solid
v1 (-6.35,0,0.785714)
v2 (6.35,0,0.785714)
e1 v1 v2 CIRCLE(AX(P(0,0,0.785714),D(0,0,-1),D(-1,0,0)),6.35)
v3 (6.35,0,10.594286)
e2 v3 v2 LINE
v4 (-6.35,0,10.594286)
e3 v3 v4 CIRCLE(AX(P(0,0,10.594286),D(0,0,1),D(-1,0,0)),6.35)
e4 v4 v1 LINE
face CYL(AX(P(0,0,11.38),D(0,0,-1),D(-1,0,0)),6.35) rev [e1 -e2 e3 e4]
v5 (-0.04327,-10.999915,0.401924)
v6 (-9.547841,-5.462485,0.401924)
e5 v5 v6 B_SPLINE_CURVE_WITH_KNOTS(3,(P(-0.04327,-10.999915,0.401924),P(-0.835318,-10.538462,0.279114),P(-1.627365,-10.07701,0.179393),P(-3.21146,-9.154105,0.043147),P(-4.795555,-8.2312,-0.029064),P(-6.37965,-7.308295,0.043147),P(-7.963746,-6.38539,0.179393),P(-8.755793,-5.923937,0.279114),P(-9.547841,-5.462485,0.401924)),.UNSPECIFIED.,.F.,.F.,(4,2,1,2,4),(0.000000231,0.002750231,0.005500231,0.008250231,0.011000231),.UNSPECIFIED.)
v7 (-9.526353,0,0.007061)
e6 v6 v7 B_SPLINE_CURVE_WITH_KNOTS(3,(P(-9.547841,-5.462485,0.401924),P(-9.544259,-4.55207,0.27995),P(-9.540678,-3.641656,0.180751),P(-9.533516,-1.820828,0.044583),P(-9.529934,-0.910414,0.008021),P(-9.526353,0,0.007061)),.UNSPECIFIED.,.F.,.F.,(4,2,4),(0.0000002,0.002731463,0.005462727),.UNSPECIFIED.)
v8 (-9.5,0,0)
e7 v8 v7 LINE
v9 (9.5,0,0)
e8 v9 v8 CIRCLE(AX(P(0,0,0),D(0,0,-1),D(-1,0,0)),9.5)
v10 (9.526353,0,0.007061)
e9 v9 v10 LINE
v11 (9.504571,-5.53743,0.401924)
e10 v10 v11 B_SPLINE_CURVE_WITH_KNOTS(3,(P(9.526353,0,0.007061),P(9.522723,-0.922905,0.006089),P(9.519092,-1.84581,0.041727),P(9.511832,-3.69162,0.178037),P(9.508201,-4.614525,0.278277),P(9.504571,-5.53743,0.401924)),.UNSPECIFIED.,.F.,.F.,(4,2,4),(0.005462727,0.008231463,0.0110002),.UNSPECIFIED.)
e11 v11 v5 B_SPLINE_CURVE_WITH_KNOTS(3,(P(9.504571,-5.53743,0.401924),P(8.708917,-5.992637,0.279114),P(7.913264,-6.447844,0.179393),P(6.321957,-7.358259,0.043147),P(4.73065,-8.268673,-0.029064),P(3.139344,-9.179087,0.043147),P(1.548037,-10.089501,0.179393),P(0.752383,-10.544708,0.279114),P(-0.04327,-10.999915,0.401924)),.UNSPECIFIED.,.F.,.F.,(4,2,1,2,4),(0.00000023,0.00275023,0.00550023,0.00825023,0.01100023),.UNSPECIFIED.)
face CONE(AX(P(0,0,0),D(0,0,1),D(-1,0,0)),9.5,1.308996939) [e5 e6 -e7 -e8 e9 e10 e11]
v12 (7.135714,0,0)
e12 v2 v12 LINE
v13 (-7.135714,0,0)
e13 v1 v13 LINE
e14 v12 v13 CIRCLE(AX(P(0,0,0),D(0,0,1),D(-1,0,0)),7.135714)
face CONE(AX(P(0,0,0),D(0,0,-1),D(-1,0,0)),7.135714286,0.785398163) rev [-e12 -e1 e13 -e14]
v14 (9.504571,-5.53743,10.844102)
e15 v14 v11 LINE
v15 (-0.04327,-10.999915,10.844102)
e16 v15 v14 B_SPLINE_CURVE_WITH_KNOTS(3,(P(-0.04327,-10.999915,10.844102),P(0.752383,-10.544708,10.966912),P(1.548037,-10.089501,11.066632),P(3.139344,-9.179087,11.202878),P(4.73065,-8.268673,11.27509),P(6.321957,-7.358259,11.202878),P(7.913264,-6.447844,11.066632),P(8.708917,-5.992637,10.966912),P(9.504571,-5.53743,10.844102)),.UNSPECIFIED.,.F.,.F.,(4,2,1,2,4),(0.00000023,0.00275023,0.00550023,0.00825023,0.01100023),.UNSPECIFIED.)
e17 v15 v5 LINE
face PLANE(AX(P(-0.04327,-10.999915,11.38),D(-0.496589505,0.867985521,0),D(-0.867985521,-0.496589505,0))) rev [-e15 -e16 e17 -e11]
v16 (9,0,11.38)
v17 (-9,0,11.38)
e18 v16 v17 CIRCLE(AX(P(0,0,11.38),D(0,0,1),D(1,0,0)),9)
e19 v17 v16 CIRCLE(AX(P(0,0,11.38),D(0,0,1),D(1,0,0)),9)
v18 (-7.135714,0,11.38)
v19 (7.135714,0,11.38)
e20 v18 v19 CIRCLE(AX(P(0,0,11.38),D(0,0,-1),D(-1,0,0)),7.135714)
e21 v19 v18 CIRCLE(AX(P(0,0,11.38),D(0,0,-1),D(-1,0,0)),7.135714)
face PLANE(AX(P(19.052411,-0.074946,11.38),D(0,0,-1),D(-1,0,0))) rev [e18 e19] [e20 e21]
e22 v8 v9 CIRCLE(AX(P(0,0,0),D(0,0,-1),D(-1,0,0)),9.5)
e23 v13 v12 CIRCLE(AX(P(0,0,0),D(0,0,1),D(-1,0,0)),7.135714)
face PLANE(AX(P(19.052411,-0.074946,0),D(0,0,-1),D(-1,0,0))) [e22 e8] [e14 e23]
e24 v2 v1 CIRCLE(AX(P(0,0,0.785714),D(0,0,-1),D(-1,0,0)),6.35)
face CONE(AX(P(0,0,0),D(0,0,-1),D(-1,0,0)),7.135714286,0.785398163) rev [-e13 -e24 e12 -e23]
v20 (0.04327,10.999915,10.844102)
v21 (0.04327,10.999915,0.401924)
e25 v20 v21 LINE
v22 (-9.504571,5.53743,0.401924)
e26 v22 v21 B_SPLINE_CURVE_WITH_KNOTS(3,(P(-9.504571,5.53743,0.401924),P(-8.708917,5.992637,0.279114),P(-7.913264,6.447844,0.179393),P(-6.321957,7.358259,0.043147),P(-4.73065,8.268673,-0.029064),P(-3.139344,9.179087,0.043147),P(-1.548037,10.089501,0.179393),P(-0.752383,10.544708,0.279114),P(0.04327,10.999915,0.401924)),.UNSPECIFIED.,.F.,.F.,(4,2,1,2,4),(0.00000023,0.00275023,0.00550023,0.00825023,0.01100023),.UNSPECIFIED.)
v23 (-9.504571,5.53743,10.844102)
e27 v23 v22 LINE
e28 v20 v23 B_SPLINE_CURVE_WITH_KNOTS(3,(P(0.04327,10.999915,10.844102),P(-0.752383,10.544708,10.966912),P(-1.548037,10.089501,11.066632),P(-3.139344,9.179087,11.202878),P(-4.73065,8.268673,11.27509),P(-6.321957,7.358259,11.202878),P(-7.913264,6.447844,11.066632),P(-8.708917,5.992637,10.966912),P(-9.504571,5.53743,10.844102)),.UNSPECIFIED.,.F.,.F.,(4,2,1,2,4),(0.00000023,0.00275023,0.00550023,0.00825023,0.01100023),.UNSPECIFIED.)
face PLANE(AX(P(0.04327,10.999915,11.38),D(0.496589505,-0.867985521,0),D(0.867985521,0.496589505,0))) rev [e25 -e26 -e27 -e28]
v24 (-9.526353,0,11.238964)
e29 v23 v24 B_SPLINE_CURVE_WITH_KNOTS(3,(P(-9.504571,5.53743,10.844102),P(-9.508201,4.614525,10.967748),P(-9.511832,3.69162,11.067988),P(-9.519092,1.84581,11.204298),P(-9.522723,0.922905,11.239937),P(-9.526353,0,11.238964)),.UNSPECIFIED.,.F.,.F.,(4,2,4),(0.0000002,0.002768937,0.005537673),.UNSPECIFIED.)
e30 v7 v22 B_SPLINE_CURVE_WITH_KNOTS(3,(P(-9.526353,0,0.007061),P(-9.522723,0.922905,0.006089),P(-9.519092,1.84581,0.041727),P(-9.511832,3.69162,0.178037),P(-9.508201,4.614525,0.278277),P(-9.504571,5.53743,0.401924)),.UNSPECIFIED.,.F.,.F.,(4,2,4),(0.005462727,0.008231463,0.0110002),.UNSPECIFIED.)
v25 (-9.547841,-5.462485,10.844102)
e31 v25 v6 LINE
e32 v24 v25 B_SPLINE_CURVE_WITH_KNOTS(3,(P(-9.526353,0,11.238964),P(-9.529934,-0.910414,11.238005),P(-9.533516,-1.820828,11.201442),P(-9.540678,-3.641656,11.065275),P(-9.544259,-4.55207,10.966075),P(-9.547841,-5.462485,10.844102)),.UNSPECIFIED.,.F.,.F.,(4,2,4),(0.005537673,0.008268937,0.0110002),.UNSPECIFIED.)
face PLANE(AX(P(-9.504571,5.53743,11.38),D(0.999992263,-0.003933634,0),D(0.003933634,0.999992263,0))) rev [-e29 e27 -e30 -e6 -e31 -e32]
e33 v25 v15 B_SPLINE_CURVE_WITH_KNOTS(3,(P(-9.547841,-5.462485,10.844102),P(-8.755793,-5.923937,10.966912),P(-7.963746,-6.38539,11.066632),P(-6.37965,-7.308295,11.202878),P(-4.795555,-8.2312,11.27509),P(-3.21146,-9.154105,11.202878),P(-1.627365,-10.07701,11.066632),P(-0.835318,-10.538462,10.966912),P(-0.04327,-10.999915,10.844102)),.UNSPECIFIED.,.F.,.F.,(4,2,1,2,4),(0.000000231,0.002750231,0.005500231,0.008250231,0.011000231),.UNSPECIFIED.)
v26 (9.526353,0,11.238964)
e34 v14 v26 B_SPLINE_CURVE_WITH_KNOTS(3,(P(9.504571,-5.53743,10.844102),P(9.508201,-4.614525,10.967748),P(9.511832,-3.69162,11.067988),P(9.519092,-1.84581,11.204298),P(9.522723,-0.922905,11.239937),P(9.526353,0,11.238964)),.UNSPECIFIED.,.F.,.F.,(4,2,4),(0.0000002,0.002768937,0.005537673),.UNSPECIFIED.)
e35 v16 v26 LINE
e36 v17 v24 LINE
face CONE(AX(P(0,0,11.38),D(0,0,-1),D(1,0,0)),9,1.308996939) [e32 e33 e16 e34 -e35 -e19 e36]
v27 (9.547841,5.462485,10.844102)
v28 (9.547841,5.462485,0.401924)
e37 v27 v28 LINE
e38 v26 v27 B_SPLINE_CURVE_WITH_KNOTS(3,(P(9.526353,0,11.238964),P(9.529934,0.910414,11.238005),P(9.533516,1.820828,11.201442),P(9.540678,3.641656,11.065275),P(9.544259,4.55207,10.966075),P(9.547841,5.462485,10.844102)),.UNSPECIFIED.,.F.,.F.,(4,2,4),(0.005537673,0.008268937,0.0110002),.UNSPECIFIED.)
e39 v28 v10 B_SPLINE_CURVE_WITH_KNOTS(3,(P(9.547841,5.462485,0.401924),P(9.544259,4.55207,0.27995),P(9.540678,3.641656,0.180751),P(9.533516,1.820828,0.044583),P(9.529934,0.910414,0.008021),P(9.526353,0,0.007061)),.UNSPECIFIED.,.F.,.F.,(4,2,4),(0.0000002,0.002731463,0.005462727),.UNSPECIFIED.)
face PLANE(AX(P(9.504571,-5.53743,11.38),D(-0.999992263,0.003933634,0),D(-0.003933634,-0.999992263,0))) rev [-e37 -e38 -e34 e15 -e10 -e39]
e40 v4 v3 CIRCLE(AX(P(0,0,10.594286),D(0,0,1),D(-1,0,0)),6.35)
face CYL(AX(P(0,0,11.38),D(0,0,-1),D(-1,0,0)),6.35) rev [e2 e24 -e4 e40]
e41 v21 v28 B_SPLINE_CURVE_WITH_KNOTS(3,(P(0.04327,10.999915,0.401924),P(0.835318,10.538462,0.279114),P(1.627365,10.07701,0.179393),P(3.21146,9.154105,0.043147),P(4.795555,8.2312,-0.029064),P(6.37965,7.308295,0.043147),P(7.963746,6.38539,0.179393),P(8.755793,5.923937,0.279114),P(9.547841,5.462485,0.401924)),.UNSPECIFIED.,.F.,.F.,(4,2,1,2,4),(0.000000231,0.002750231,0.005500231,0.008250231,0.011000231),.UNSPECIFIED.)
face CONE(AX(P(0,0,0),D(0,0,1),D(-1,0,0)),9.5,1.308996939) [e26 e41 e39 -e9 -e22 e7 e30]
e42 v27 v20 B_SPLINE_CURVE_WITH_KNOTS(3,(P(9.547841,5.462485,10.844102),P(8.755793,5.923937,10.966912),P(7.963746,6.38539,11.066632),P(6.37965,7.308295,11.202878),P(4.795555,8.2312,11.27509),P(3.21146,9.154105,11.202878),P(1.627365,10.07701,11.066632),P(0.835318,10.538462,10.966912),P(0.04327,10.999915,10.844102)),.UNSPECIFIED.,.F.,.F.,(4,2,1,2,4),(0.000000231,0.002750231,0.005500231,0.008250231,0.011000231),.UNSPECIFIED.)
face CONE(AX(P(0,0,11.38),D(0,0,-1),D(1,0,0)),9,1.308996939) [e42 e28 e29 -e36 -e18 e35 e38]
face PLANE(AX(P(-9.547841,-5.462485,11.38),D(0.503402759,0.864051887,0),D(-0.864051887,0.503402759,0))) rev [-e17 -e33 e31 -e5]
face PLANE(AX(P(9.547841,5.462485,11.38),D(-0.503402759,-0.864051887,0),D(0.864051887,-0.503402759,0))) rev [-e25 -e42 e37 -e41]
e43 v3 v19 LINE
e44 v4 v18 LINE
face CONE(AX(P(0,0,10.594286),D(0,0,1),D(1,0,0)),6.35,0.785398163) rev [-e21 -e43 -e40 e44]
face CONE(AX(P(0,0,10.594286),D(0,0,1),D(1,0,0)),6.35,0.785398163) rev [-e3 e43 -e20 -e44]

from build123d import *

# Parameters (mm, degrees)
SKETCH1_R          = 6.35
BASE_EXTRUDE_DEPTH = 11.38
SKETCH2_OUTSIDE_W  = 172.782
SKETCH2_OUTSIDE_H  = 175.686
SKETCH2_OUTSIDE_R  = 9.5
CUT_EXTRUDE1_DEPTH = 19.484149703
CUT_EXTRUDE1_DRAFT = -75
SKETCH3_OUTSIDE_W  = 172.782
SKETCH3_OUTSIDE_H  = 175.686
SKETCH3_OUTSIDE_R  = 9
CUT_EXTRUDE2_DEPTH = 19.484149703
CUT_EXTRUDE2_DRAFT = -75
CHAMFER1_SIZE      = 0.785714286


with BuildPart() as part:
    # Sketch1 → Base-Extrude (new body)
    with BuildSketch(Plane.XY):
        Polygon((0.043269974, 10.999914896), (-9.504570752, 5.537430344), (-9.547840726, -5.462484551), (-0.043269974, -10.999914896), (9.504570752, -5.537430344), (9.547840726, 5.462484551), align=None)
        Circle(SKETCH1_R, mode=Mode.SUBTRACT)
    extrude(amount=BASE_EXTRUDE_DEPTH)


with BuildPart() as cut_extrude1_tool:
    # Sketch2 outside → Cut-Extrude1 (with draft: the straight prism first)
    with BuildSketch(Plane(origin=(0, 0, 0), x_dir=(-1, 0, 0), z_dir=(0, 0, -1))):
        Rectangle(SKETCH2_OUTSIDE_W, SKETCH2_OUTSIDE_H)
        Circle(SKETCH2_OUTSIDE_R, mode=Mode.SUBTRACT)
    extrude(amount=-CUT_EXTRUDE1_DEPTH)
    # Cut-Extrude1: the draft: its side faces are tilted about the plane it starts from
    cut_extrude1_sides = [cut_extrude1_tool.faces().sort_by_distance(p)[0] for p in [
        (0, -87.843, 9.742074851),
        (-86.391, 0, 9.742074851),
        (0, 87.843, 9.742074851),
        (86.391, 0, 9.742074851),
        (9.5, 0, 9.742074851),
    ]]
    draft(cut_extrude1_sides, Plane(origin=(0, 0, 0), x_dir=(-1, 0, 0), z_dir=(0, 0, -1)), CUT_EXTRUDE1_DRAFT)


with BuildPart() as part_1:
    add(part.part)

    # Cut-Extrude1: cut by cut_extrude1_tool
    add(cut_extrude1_tool.part, mode=Mode.SUBTRACT)


with BuildPart() as cut_extrude2_tool:
    # Sketch3 outside → Cut-Extrude2 (with draft: the straight prism first)
    with BuildSketch(Plane.XY.offset(11.38)):
        Rectangle(SKETCH3_OUTSIDE_W, SKETCH3_OUTSIDE_H)
        Circle(SKETCH3_OUTSIDE_R, mode=Mode.SUBTRACT)
    extrude(amount=-CUT_EXTRUDE2_DEPTH)
    # Cut-Extrude2: the draft: its side faces are tilted about the plane it starts from
    cut_extrude2_sides = [cut_extrude2_tool.faces().sort_by_distance(p)[0] for p in [
        (0, -87.843, 1.637925149),
        (86.391, 0, 1.637925149),
        (0, 87.843, 1.637925149),
        (-86.391, 0, 1.637925149),
        (-9, 0, 1.637925149),
    ]]
    draft(cut_extrude2_sides, Plane.XY.offset(11.38), CUT_EXTRUDE2_DRAFT)


with BuildPart() as part_2:
    add(part_1.part)

    # Cut-Extrude2: cut by cut_extrude2_tool
    add(cut_extrude2_tool.part, mode=Mode.SUBTRACT)

    # Chamfer1
    chamfer1_edges = [part_2.edges().sort_by_distance(p)[0] for p in [
        (-6.35, 0, 0),
        (-6.35, 0, 11.38),
    ]]
    chamfer(chamfer1_edges, length=CHAMFER1_SIZE)


solid = part_2.part
